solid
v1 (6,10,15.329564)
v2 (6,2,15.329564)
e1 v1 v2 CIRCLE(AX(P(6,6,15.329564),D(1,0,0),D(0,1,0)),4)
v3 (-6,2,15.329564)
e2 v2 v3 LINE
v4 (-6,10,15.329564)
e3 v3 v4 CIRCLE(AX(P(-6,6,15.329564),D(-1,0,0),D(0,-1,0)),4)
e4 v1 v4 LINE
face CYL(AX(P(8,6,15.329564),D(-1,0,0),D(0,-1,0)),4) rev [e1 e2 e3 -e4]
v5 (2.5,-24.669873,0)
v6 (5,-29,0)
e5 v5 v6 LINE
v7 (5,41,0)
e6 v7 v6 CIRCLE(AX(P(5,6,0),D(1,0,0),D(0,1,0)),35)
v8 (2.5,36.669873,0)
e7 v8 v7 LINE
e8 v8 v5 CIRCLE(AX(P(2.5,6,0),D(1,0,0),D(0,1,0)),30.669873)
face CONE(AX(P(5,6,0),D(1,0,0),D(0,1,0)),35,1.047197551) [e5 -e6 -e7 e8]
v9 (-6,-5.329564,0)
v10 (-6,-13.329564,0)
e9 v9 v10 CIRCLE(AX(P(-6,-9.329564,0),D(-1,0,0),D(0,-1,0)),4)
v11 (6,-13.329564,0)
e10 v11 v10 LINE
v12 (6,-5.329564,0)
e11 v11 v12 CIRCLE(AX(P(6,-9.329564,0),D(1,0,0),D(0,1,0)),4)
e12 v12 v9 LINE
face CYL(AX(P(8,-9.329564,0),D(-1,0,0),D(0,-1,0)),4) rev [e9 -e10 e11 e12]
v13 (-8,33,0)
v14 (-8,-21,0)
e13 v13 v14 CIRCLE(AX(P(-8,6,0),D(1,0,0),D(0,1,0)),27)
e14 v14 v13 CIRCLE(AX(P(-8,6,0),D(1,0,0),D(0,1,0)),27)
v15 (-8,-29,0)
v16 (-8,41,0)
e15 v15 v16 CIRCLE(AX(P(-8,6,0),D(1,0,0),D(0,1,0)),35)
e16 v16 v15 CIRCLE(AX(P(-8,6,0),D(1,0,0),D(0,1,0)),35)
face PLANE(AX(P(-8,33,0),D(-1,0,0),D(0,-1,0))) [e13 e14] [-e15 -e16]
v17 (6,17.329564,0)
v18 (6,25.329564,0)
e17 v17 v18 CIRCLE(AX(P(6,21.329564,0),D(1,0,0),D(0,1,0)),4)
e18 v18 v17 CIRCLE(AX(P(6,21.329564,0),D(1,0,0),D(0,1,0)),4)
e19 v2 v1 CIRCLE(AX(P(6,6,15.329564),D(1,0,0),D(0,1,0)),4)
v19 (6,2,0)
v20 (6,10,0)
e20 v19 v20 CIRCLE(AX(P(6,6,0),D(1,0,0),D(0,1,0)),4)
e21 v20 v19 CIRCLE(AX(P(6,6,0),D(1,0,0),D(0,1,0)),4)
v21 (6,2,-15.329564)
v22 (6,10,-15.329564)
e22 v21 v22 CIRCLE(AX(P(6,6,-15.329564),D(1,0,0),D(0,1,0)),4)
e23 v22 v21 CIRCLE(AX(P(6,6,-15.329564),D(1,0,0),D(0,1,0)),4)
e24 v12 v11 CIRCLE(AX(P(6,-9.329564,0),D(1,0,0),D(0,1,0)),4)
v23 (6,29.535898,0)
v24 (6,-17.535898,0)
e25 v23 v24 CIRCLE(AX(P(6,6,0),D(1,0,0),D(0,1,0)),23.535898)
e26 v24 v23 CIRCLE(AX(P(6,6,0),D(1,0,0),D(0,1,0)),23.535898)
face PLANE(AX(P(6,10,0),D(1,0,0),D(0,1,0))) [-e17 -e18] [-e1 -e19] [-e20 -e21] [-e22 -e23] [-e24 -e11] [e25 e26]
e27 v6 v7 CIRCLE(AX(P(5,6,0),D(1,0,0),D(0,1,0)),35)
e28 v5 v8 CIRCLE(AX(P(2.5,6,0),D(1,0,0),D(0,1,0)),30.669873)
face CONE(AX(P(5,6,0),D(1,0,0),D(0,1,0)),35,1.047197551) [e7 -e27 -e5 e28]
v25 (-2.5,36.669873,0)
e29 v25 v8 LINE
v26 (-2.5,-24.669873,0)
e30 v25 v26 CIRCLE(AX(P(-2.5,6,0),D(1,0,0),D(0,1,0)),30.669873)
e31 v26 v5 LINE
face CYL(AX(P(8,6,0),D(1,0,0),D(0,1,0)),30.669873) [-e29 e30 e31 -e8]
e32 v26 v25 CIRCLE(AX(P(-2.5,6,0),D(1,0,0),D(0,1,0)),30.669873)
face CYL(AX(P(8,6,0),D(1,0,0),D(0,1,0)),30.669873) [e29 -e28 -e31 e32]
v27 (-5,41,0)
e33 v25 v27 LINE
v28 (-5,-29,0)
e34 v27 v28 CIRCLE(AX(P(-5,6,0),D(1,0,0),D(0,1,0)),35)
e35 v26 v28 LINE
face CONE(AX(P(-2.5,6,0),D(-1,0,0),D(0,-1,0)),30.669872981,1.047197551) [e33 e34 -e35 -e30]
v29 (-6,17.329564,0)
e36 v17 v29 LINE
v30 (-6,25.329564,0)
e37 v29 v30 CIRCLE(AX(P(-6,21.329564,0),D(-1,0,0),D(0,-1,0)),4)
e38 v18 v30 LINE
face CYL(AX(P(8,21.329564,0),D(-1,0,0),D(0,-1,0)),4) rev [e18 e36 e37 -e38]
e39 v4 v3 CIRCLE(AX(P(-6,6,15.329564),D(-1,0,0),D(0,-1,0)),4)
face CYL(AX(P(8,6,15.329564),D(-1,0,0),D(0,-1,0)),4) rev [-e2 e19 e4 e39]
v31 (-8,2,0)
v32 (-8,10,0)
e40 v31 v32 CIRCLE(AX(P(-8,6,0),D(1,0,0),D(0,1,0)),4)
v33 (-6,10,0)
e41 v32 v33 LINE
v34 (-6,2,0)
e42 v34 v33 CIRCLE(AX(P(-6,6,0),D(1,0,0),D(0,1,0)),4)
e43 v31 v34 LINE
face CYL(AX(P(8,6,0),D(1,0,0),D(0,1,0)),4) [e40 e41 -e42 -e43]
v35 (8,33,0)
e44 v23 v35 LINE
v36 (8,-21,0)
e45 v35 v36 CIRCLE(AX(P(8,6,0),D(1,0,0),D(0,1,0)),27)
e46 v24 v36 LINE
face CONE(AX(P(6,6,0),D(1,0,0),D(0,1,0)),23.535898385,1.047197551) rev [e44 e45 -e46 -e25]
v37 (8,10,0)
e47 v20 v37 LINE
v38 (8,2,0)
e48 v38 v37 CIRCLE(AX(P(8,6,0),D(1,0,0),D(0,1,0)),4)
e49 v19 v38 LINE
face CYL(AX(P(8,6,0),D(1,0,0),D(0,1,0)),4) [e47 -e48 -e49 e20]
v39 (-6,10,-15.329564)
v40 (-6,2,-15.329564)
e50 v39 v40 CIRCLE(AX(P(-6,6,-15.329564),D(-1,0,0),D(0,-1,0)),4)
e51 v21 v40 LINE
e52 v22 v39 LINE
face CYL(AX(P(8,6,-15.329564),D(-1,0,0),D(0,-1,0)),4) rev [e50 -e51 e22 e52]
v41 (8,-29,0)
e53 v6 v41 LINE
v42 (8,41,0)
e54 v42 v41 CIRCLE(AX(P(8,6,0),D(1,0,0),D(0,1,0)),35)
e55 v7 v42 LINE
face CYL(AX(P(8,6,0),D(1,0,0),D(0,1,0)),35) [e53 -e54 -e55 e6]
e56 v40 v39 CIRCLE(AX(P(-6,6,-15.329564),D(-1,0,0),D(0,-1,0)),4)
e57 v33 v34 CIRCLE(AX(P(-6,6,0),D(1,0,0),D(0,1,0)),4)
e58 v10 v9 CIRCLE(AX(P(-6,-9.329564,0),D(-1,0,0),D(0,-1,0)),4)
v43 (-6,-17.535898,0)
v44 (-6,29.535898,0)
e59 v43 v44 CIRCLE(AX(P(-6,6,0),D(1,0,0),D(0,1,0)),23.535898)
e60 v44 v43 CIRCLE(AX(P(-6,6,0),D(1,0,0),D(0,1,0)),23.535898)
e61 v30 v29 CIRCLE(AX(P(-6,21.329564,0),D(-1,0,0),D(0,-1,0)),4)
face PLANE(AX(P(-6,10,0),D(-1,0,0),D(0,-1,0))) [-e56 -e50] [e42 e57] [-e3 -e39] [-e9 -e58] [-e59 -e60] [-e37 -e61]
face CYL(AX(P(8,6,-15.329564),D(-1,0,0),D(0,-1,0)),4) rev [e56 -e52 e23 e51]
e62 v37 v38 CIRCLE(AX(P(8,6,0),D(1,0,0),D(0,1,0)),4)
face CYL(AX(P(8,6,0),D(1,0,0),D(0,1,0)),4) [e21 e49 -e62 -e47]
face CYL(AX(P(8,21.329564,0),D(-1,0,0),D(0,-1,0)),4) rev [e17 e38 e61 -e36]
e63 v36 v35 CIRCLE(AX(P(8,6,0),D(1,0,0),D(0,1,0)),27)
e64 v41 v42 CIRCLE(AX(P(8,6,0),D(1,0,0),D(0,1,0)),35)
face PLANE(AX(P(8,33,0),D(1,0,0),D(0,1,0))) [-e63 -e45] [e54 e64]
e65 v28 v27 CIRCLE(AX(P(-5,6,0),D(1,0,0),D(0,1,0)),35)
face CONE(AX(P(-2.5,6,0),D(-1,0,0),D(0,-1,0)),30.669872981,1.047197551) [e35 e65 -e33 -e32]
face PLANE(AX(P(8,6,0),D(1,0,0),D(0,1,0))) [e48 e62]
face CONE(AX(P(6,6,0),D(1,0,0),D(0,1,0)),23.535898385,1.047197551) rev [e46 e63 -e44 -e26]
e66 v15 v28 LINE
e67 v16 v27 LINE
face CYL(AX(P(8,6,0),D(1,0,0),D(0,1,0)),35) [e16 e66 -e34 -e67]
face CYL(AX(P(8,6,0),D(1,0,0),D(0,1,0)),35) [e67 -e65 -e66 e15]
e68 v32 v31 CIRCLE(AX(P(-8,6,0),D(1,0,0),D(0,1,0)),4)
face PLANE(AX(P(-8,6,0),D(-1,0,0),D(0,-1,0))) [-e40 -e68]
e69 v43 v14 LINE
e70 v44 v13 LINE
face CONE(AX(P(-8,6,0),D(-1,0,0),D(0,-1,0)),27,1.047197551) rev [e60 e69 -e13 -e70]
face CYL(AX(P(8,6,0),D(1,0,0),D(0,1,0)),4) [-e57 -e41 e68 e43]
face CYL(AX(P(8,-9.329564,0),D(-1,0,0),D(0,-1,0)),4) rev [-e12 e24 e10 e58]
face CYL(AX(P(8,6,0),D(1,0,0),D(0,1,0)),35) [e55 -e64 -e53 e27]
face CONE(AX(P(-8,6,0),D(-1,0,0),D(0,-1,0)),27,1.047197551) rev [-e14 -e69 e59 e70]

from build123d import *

# Parameters (mm, degrees)
HUB_HOLES_SKETCH_R = 4
HUB_HOLES_8_DEPTH  = 56.695601263


with BuildPart() as part:
    # Pulley Profile Sketch → Pulley Body (revolve)
    with BuildSketch(Plane.XY):
        Polygon((8, 6), (-8, 6), (-8, 10), (-6, 10), (-6, 29.535898385), (-8, 33), (-8, 41), (-5, 41), (-2.5, 36.669872981), (2.5, 36.669872981), (5, 41), (8, 41), (8, 33), (6, 29.535898385), (6, 10), (8, 10), align=None)
    revolve(axis=Axis((8, 6, 0), (-1, 0, 0)))

    # Hub Holes Sketch → Hub Holes Ø8 (cut, through all)
    with BuildSketch(Plane.ZY.offset(6)):
        with Locations(Location((0, 21.329563784, 0), (0, 0, 270))):
            Circle(HUB_HOLES_SKETCH_R)
        with Locations(Location((-15.329563784, 6, 0), (0, 0, 270))):
            Circle(HUB_HOLES_SKETCH_R)
        with Locations(Location((15.329563784, 6, 0), (0, 0, 270))):
            Circle(HUB_HOLES_SKETCH_R)
        with Locations(Location((0, -9.329563784, 0), (0, 0, 270))):
            Circle(HUB_HOLES_SKETCH_R)
    extrude(amount=-HUB_HOLES_8_DEPTH, mode=Mode.SUBTRACT)


solid = part.part
